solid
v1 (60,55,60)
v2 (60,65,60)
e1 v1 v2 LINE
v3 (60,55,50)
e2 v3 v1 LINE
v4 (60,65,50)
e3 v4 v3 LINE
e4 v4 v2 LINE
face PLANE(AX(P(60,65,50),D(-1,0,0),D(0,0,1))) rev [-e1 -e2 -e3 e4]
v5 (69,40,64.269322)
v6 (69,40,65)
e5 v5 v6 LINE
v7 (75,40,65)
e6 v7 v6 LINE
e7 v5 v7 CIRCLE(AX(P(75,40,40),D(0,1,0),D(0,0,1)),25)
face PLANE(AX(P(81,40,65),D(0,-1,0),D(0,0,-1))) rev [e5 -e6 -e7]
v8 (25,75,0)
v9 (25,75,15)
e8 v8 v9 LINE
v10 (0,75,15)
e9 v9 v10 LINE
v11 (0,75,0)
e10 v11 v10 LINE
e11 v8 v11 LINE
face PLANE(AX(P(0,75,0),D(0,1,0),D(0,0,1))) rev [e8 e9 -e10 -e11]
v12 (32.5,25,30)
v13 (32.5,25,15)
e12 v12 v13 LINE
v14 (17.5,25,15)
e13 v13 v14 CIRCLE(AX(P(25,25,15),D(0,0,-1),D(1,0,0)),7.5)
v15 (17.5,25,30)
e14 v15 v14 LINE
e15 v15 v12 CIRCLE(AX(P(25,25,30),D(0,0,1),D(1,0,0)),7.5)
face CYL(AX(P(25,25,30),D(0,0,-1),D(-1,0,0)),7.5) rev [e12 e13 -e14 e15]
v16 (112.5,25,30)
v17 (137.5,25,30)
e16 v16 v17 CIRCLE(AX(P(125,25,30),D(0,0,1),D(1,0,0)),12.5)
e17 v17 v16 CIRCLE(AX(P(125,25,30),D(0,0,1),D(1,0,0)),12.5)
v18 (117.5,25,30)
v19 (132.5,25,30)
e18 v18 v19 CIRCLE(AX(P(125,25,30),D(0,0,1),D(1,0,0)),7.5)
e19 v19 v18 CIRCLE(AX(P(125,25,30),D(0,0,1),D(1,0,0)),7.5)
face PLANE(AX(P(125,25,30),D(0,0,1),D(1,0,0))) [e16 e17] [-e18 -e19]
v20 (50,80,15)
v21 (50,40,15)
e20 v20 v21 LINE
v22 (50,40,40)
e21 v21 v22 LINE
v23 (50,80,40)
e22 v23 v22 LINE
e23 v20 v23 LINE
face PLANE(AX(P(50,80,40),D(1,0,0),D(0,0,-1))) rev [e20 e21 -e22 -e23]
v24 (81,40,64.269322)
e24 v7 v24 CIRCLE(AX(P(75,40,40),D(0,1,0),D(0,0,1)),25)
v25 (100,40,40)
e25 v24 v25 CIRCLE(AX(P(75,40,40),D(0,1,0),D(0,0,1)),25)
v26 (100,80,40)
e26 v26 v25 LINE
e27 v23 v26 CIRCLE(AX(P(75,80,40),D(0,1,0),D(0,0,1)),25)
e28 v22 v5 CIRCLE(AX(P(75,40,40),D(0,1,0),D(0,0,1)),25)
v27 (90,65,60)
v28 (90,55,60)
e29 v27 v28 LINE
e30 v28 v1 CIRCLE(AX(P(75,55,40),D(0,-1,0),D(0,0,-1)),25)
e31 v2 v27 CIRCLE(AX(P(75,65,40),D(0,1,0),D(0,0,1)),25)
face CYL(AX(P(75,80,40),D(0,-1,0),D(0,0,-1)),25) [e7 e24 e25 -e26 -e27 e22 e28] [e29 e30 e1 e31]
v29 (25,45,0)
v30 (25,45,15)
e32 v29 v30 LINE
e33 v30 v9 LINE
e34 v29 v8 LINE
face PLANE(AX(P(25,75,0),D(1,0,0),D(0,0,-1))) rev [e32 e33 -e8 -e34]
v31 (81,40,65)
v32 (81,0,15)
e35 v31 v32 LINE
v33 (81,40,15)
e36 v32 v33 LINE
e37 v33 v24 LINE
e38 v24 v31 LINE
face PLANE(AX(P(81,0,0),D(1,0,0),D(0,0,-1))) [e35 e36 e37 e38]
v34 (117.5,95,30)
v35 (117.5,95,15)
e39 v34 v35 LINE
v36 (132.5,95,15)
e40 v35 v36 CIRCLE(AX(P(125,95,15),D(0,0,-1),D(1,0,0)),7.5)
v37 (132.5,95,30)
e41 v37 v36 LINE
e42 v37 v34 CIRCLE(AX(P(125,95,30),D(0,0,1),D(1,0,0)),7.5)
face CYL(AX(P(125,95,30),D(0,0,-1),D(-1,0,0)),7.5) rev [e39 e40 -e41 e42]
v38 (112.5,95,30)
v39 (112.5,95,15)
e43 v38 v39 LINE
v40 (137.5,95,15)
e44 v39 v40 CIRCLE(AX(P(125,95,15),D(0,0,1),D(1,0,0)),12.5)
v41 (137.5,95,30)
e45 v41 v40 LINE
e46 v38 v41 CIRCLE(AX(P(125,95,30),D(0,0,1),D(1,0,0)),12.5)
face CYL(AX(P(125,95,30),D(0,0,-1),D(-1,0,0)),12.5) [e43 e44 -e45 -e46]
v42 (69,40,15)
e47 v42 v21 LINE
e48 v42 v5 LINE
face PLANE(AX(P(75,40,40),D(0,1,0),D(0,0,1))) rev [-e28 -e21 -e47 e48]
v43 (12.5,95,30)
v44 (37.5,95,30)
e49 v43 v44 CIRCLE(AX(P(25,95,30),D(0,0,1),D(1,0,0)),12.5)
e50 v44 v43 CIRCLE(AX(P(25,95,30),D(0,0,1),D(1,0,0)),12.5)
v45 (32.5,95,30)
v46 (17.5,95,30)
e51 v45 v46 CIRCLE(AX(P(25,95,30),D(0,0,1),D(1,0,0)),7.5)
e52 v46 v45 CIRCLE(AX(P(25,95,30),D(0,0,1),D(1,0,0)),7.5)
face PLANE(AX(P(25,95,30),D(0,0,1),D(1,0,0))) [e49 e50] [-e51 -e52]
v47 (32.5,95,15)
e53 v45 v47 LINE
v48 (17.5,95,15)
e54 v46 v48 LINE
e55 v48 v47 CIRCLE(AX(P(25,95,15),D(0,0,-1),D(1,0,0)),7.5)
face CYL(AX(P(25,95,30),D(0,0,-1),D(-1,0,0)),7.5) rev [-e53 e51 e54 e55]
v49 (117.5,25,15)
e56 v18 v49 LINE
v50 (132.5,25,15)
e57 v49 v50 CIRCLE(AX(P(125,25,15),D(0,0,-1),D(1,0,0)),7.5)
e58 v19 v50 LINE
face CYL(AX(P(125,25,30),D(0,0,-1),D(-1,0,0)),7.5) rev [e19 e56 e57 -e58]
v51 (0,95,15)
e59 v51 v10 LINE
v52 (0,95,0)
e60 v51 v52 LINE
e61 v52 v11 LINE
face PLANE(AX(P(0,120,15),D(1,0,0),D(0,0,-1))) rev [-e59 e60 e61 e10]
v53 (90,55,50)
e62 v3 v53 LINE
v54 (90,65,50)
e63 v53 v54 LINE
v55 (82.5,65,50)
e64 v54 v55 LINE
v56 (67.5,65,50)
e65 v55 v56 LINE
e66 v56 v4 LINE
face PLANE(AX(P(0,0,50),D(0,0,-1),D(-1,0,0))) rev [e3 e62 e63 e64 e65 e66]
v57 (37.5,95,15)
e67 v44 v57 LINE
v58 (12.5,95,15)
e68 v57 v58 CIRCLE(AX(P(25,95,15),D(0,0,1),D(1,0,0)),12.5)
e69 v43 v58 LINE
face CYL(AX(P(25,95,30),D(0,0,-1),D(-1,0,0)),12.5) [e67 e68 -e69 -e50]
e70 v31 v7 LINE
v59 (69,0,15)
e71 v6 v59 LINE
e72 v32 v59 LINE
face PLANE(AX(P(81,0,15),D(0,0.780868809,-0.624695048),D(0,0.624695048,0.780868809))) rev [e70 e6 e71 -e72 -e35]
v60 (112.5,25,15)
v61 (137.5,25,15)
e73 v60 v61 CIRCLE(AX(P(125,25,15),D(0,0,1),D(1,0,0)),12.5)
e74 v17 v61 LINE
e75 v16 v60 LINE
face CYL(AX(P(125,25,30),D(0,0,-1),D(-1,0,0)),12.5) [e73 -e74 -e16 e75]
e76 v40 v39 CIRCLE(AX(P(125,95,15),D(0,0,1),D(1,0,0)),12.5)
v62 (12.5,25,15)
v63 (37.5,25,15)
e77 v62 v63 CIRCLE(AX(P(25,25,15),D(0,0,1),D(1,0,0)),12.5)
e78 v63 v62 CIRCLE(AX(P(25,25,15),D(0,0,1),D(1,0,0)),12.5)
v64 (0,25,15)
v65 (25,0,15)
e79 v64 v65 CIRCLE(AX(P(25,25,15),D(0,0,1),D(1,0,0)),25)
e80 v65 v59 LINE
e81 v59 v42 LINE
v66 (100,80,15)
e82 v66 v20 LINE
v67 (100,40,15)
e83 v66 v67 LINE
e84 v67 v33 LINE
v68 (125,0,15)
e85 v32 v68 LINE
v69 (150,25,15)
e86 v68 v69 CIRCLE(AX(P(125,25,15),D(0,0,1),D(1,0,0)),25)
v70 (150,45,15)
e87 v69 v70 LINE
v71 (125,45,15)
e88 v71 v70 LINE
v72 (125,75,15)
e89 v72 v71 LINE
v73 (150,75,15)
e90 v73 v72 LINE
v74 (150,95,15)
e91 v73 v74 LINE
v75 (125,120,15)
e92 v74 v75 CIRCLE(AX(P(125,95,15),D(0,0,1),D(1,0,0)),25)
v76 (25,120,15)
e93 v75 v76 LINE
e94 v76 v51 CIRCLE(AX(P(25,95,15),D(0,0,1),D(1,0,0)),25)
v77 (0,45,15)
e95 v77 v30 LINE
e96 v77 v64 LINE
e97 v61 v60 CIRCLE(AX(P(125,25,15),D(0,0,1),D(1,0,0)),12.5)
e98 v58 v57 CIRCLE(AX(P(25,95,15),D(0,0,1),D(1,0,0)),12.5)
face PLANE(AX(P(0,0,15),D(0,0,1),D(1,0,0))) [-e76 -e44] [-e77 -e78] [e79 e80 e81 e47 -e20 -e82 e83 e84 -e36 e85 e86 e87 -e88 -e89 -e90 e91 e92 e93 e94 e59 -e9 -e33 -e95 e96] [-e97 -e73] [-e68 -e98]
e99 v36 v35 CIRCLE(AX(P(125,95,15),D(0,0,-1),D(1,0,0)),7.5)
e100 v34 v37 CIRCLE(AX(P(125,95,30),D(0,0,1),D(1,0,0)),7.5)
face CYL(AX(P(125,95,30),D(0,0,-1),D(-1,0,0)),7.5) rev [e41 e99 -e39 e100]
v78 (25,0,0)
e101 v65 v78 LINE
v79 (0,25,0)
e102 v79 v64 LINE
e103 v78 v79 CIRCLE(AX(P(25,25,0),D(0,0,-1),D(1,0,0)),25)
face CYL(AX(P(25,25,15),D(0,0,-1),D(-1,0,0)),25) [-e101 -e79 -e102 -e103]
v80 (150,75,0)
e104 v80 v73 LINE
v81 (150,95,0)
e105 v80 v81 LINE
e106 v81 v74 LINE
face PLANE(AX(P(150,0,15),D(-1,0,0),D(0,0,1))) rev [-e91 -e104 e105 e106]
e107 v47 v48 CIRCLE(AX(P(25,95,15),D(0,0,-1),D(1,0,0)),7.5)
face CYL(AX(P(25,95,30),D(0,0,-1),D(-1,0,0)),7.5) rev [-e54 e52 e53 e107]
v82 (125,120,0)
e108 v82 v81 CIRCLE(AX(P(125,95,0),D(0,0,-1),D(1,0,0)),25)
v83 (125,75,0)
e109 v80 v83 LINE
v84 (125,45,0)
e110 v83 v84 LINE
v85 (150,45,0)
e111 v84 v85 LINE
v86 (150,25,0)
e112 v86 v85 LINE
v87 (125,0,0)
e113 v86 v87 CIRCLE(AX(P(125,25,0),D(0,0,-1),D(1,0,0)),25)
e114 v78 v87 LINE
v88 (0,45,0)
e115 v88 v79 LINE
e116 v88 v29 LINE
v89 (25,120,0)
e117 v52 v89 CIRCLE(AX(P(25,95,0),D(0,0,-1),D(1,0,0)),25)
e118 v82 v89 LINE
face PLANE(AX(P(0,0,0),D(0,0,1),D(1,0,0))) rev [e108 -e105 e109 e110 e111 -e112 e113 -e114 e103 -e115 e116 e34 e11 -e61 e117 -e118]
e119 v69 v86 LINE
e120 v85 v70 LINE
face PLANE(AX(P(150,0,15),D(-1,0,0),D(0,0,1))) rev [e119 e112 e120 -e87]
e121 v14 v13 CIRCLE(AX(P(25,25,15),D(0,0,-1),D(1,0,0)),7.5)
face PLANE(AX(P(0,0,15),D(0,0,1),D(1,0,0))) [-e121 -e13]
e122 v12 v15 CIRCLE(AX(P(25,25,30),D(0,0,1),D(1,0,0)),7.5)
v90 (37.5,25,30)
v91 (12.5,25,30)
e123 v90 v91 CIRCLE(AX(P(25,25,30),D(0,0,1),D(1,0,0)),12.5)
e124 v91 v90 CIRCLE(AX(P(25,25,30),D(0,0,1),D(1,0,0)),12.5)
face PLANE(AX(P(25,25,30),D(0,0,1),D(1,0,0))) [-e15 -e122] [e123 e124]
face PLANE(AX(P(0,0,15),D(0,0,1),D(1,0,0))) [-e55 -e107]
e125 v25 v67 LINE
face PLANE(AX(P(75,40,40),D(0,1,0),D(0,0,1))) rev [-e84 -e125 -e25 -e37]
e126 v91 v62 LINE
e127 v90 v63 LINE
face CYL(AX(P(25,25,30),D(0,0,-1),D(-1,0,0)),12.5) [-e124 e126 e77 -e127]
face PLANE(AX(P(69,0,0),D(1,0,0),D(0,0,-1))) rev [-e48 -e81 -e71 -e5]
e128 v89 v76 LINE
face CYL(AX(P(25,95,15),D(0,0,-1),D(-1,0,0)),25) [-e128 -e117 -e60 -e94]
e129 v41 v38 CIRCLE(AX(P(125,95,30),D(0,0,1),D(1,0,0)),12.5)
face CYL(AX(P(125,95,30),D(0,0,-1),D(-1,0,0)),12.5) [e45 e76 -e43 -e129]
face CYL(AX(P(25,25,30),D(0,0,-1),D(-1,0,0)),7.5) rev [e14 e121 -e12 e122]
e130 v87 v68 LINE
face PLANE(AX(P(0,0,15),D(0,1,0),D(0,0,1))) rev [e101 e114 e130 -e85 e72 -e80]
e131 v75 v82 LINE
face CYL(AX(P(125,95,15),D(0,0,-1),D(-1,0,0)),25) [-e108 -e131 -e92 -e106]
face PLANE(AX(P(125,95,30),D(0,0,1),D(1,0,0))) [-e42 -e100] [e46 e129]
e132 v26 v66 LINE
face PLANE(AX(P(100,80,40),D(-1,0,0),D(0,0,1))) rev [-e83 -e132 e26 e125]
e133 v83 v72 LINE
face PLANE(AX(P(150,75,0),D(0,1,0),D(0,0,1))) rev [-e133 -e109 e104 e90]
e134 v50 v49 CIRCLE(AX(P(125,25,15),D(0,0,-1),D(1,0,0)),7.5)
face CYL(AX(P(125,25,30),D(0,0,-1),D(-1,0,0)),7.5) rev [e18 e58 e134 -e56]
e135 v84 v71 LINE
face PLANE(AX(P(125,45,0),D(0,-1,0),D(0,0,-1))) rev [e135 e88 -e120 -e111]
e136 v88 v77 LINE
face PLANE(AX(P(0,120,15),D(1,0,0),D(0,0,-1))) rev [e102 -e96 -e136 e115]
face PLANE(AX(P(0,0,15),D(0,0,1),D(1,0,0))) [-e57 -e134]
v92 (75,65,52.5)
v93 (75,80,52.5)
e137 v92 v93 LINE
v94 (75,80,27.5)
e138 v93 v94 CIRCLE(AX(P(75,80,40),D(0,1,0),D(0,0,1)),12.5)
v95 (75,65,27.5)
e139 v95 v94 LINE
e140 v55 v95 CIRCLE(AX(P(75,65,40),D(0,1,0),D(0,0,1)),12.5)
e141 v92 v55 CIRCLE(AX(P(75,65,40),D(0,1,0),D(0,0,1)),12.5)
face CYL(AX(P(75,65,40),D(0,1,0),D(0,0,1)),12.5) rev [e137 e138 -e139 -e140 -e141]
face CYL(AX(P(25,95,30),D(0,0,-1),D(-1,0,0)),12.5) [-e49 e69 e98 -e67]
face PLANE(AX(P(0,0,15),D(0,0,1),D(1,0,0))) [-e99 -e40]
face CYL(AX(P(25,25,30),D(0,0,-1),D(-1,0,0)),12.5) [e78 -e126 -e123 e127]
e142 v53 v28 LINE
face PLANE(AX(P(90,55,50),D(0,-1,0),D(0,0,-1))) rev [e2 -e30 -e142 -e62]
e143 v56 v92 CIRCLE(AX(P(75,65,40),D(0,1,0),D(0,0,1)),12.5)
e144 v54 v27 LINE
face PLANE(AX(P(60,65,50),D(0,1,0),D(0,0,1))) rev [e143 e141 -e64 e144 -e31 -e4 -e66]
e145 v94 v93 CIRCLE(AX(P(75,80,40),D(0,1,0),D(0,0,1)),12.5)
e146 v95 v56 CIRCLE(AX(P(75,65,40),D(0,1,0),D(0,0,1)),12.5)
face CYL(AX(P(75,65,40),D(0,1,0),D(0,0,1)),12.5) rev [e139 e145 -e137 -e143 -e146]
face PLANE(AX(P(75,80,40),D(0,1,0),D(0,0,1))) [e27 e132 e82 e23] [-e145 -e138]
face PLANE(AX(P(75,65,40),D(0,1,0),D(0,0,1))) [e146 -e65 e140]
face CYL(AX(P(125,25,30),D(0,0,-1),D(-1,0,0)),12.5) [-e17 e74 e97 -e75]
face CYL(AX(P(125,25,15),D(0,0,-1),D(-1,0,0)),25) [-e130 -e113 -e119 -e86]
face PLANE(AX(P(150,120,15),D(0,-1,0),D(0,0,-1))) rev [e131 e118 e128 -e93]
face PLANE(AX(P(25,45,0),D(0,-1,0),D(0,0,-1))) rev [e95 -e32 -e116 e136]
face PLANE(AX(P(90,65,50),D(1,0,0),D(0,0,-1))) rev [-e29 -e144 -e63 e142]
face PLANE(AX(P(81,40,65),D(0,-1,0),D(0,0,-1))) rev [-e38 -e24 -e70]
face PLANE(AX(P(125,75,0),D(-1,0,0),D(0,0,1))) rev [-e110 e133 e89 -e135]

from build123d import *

# Parameters (mm, degrees)
BASE_PLATE_SKETCH_W         = 150
BASE_PLATE_SKETCH_H         = 120
BASE_PLATE_150X120X15_DEPTH = 15
RAISED_BOSS_SKETCH_R        = 12.5
RAISED_BOSS_SKETCH_R_2      = 7.5
RAISED_BOSS_15MM_DEPTH      = 15
BEARING_BLOCK_DEPTH         = 20
RELIEF_CUT_SKETCH_W         = 25
RELIEF_CUT_SKETCH_H         = 30
RELIEF_CUT_DEPTH            = 15
PLATE_CORNER_FILLETS_R25_R  = 25
BLOCK_SLOT_SKETCH_W         = 30
BLOCK_SLOT_SKETCH_H         = 10
BLOCK_SLOT_30X10_DEPTH      = 15
SUPPORT_RIB_DEPTH           = 6
BEARING_BORE_SKETCH_R       = 12.5
BEARING_BORE_25_DEPTH       = 15


with BuildPart() as part:
    # Base Plate Sketch → Base Plate 150x120x15 (new body)
    with BuildSketch(Plane.XY):
        with Locations((75, 60)):
            Rectangle(BASE_PLATE_SKETCH_W, BASE_PLATE_SKETCH_H)
    extrude(amount=BASE_PLATE_150X120X15_DEPTH)

    # Raised Boss Sketch → Raised Boss 15mm (add)
    # profile 1 of 4: a face of its own
    with BuildSketch(Plane.XY.offset(15)):
        with Locations((25, 95)):
            Circle(RAISED_BOSS_SKETCH_R)
        with Locations((25, 95)):
            Circle(RAISED_BOSS_SKETCH_R_2, mode=Mode.SUBTRACT)
    # profile 2 of 4: a face of its own
    with BuildSketch(Plane.XY.offset(15)):
        with Locations((125, 95)):
            Circle(RAISED_BOSS_SKETCH_R)
        with Locations((125, 95)):
            Circle(RAISED_BOSS_SKETCH_R_2, mode=Mode.SUBTRACT)
    # profile 3 of 4: a face of its own
    with BuildSketch(Plane.XY.offset(15)):
        with Locations((125, 25)):
            Circle(RAISED_BOSS_SKETCH_R)
        with Locations((125, 25)):
            Circle(RAISED_BOSS_SKETCH_R_2, mode=Mode.SUBTRACT)
    # profile 4 of 4: a face of its own
    with BuildSketch(Plane.XY.offset(15)):
        with Locations((25, 25)):
            Circle(RAISED_BOSS_SKETCH_R)
        with Locations((25, 25)):
            Circle(RAISED_BOSS_SKETCH_R_2, mode=Mode.SUBTRACT)
    extrude(amount=RAISED_BOSS_15MM_DEPTH)

    # Bearing Block Sketch → Bearing Block (add, symmetric)
    with BuildSketch(Plane(origin=(0, 60, 0), x_dir=(1, 0, 0), z_dir=(0, 1, 0))):
        with BuildLine():
            Line((50, -40), (50, -15))
            Line((50, -15), (100, -15))
            Line((100, -15), (100, -40))
            ThreePointArc((100, -40), (75, -65), (50, -40))
        make_face()
    extrude(amount=BEARING_BLOCK_DEPTH, both=True)

    # Relief Cut Sketch → Relief Cut (cut)
    with BuildSketch(Plane.XY.offset(15)):
        Polygon((150, 60), (150, 75), (125, 75), (125, 45), (150, 45), align=None)
        with Locations((12.5, 60)):
            Rectangle(RELIEF_CUT_SKETCH_W, RELIEF_CUT_SKETCH_H)
    extrude(amount=-RELIEF_CUT_DEPTH, mode=Mode.SUBTRACT)

    # Plate Corner Fillets R25
    plate_corner_fillets_r25_edges = [part.edges().sort_by_distance(p)[0] for p in [
        (0, 120, 7.5),
        (150, 120, 7.5),
        (150, 0, 7.5),
        (0, 0, 7.5),
    ]]
    fillet(plate_corner_fillets_r25_edges, radius=PLATE_CORNER_FILLETS_R25_R)

    # Block Slot Sketch → Block Slot 30x10 (cut)
    with BuildSketch(Plane.XY.offset(65)):
        with Locations((75, 60)):
            Rectangle(BLOCK_SLOT_SKETCH_W, BLOCK_SLOT_SKETCH_H)
    extrude(amount=-BLOCK_SLOT_30X10_DEPTH, mode=Mode.SUBTRACT)

    # Support Rib Sketch → Support Rib (add, symmetric)
    with BuildSketch(Plane(origin=(75, 0, 0), x_dir=(0, 0, -1), z_dir=(1, 0, 0))):
        Polygon((-15, 0), (-65, 40), (-15, 40), align=None)
    extrude(amount=SUPPORT_RIB_DEPTH, both=True)

    # Bearing Bore Sketch → Bearing Bore Ø25 (cut)
    with BuildSketch(Plane(origin=(0, 80, 0), x_dir=(1, 0, 0), z_dir=(0, 1, 0))):
        with Locations(Location((75, -40, 0), (0, 0, 270))):
            Circle(BEARING_BORE_SKETCH_R)
    extrude(amount=-BEARING_BORE_25_DEPTH, mode=Mode.SUBTRACT)


solid = part.part
